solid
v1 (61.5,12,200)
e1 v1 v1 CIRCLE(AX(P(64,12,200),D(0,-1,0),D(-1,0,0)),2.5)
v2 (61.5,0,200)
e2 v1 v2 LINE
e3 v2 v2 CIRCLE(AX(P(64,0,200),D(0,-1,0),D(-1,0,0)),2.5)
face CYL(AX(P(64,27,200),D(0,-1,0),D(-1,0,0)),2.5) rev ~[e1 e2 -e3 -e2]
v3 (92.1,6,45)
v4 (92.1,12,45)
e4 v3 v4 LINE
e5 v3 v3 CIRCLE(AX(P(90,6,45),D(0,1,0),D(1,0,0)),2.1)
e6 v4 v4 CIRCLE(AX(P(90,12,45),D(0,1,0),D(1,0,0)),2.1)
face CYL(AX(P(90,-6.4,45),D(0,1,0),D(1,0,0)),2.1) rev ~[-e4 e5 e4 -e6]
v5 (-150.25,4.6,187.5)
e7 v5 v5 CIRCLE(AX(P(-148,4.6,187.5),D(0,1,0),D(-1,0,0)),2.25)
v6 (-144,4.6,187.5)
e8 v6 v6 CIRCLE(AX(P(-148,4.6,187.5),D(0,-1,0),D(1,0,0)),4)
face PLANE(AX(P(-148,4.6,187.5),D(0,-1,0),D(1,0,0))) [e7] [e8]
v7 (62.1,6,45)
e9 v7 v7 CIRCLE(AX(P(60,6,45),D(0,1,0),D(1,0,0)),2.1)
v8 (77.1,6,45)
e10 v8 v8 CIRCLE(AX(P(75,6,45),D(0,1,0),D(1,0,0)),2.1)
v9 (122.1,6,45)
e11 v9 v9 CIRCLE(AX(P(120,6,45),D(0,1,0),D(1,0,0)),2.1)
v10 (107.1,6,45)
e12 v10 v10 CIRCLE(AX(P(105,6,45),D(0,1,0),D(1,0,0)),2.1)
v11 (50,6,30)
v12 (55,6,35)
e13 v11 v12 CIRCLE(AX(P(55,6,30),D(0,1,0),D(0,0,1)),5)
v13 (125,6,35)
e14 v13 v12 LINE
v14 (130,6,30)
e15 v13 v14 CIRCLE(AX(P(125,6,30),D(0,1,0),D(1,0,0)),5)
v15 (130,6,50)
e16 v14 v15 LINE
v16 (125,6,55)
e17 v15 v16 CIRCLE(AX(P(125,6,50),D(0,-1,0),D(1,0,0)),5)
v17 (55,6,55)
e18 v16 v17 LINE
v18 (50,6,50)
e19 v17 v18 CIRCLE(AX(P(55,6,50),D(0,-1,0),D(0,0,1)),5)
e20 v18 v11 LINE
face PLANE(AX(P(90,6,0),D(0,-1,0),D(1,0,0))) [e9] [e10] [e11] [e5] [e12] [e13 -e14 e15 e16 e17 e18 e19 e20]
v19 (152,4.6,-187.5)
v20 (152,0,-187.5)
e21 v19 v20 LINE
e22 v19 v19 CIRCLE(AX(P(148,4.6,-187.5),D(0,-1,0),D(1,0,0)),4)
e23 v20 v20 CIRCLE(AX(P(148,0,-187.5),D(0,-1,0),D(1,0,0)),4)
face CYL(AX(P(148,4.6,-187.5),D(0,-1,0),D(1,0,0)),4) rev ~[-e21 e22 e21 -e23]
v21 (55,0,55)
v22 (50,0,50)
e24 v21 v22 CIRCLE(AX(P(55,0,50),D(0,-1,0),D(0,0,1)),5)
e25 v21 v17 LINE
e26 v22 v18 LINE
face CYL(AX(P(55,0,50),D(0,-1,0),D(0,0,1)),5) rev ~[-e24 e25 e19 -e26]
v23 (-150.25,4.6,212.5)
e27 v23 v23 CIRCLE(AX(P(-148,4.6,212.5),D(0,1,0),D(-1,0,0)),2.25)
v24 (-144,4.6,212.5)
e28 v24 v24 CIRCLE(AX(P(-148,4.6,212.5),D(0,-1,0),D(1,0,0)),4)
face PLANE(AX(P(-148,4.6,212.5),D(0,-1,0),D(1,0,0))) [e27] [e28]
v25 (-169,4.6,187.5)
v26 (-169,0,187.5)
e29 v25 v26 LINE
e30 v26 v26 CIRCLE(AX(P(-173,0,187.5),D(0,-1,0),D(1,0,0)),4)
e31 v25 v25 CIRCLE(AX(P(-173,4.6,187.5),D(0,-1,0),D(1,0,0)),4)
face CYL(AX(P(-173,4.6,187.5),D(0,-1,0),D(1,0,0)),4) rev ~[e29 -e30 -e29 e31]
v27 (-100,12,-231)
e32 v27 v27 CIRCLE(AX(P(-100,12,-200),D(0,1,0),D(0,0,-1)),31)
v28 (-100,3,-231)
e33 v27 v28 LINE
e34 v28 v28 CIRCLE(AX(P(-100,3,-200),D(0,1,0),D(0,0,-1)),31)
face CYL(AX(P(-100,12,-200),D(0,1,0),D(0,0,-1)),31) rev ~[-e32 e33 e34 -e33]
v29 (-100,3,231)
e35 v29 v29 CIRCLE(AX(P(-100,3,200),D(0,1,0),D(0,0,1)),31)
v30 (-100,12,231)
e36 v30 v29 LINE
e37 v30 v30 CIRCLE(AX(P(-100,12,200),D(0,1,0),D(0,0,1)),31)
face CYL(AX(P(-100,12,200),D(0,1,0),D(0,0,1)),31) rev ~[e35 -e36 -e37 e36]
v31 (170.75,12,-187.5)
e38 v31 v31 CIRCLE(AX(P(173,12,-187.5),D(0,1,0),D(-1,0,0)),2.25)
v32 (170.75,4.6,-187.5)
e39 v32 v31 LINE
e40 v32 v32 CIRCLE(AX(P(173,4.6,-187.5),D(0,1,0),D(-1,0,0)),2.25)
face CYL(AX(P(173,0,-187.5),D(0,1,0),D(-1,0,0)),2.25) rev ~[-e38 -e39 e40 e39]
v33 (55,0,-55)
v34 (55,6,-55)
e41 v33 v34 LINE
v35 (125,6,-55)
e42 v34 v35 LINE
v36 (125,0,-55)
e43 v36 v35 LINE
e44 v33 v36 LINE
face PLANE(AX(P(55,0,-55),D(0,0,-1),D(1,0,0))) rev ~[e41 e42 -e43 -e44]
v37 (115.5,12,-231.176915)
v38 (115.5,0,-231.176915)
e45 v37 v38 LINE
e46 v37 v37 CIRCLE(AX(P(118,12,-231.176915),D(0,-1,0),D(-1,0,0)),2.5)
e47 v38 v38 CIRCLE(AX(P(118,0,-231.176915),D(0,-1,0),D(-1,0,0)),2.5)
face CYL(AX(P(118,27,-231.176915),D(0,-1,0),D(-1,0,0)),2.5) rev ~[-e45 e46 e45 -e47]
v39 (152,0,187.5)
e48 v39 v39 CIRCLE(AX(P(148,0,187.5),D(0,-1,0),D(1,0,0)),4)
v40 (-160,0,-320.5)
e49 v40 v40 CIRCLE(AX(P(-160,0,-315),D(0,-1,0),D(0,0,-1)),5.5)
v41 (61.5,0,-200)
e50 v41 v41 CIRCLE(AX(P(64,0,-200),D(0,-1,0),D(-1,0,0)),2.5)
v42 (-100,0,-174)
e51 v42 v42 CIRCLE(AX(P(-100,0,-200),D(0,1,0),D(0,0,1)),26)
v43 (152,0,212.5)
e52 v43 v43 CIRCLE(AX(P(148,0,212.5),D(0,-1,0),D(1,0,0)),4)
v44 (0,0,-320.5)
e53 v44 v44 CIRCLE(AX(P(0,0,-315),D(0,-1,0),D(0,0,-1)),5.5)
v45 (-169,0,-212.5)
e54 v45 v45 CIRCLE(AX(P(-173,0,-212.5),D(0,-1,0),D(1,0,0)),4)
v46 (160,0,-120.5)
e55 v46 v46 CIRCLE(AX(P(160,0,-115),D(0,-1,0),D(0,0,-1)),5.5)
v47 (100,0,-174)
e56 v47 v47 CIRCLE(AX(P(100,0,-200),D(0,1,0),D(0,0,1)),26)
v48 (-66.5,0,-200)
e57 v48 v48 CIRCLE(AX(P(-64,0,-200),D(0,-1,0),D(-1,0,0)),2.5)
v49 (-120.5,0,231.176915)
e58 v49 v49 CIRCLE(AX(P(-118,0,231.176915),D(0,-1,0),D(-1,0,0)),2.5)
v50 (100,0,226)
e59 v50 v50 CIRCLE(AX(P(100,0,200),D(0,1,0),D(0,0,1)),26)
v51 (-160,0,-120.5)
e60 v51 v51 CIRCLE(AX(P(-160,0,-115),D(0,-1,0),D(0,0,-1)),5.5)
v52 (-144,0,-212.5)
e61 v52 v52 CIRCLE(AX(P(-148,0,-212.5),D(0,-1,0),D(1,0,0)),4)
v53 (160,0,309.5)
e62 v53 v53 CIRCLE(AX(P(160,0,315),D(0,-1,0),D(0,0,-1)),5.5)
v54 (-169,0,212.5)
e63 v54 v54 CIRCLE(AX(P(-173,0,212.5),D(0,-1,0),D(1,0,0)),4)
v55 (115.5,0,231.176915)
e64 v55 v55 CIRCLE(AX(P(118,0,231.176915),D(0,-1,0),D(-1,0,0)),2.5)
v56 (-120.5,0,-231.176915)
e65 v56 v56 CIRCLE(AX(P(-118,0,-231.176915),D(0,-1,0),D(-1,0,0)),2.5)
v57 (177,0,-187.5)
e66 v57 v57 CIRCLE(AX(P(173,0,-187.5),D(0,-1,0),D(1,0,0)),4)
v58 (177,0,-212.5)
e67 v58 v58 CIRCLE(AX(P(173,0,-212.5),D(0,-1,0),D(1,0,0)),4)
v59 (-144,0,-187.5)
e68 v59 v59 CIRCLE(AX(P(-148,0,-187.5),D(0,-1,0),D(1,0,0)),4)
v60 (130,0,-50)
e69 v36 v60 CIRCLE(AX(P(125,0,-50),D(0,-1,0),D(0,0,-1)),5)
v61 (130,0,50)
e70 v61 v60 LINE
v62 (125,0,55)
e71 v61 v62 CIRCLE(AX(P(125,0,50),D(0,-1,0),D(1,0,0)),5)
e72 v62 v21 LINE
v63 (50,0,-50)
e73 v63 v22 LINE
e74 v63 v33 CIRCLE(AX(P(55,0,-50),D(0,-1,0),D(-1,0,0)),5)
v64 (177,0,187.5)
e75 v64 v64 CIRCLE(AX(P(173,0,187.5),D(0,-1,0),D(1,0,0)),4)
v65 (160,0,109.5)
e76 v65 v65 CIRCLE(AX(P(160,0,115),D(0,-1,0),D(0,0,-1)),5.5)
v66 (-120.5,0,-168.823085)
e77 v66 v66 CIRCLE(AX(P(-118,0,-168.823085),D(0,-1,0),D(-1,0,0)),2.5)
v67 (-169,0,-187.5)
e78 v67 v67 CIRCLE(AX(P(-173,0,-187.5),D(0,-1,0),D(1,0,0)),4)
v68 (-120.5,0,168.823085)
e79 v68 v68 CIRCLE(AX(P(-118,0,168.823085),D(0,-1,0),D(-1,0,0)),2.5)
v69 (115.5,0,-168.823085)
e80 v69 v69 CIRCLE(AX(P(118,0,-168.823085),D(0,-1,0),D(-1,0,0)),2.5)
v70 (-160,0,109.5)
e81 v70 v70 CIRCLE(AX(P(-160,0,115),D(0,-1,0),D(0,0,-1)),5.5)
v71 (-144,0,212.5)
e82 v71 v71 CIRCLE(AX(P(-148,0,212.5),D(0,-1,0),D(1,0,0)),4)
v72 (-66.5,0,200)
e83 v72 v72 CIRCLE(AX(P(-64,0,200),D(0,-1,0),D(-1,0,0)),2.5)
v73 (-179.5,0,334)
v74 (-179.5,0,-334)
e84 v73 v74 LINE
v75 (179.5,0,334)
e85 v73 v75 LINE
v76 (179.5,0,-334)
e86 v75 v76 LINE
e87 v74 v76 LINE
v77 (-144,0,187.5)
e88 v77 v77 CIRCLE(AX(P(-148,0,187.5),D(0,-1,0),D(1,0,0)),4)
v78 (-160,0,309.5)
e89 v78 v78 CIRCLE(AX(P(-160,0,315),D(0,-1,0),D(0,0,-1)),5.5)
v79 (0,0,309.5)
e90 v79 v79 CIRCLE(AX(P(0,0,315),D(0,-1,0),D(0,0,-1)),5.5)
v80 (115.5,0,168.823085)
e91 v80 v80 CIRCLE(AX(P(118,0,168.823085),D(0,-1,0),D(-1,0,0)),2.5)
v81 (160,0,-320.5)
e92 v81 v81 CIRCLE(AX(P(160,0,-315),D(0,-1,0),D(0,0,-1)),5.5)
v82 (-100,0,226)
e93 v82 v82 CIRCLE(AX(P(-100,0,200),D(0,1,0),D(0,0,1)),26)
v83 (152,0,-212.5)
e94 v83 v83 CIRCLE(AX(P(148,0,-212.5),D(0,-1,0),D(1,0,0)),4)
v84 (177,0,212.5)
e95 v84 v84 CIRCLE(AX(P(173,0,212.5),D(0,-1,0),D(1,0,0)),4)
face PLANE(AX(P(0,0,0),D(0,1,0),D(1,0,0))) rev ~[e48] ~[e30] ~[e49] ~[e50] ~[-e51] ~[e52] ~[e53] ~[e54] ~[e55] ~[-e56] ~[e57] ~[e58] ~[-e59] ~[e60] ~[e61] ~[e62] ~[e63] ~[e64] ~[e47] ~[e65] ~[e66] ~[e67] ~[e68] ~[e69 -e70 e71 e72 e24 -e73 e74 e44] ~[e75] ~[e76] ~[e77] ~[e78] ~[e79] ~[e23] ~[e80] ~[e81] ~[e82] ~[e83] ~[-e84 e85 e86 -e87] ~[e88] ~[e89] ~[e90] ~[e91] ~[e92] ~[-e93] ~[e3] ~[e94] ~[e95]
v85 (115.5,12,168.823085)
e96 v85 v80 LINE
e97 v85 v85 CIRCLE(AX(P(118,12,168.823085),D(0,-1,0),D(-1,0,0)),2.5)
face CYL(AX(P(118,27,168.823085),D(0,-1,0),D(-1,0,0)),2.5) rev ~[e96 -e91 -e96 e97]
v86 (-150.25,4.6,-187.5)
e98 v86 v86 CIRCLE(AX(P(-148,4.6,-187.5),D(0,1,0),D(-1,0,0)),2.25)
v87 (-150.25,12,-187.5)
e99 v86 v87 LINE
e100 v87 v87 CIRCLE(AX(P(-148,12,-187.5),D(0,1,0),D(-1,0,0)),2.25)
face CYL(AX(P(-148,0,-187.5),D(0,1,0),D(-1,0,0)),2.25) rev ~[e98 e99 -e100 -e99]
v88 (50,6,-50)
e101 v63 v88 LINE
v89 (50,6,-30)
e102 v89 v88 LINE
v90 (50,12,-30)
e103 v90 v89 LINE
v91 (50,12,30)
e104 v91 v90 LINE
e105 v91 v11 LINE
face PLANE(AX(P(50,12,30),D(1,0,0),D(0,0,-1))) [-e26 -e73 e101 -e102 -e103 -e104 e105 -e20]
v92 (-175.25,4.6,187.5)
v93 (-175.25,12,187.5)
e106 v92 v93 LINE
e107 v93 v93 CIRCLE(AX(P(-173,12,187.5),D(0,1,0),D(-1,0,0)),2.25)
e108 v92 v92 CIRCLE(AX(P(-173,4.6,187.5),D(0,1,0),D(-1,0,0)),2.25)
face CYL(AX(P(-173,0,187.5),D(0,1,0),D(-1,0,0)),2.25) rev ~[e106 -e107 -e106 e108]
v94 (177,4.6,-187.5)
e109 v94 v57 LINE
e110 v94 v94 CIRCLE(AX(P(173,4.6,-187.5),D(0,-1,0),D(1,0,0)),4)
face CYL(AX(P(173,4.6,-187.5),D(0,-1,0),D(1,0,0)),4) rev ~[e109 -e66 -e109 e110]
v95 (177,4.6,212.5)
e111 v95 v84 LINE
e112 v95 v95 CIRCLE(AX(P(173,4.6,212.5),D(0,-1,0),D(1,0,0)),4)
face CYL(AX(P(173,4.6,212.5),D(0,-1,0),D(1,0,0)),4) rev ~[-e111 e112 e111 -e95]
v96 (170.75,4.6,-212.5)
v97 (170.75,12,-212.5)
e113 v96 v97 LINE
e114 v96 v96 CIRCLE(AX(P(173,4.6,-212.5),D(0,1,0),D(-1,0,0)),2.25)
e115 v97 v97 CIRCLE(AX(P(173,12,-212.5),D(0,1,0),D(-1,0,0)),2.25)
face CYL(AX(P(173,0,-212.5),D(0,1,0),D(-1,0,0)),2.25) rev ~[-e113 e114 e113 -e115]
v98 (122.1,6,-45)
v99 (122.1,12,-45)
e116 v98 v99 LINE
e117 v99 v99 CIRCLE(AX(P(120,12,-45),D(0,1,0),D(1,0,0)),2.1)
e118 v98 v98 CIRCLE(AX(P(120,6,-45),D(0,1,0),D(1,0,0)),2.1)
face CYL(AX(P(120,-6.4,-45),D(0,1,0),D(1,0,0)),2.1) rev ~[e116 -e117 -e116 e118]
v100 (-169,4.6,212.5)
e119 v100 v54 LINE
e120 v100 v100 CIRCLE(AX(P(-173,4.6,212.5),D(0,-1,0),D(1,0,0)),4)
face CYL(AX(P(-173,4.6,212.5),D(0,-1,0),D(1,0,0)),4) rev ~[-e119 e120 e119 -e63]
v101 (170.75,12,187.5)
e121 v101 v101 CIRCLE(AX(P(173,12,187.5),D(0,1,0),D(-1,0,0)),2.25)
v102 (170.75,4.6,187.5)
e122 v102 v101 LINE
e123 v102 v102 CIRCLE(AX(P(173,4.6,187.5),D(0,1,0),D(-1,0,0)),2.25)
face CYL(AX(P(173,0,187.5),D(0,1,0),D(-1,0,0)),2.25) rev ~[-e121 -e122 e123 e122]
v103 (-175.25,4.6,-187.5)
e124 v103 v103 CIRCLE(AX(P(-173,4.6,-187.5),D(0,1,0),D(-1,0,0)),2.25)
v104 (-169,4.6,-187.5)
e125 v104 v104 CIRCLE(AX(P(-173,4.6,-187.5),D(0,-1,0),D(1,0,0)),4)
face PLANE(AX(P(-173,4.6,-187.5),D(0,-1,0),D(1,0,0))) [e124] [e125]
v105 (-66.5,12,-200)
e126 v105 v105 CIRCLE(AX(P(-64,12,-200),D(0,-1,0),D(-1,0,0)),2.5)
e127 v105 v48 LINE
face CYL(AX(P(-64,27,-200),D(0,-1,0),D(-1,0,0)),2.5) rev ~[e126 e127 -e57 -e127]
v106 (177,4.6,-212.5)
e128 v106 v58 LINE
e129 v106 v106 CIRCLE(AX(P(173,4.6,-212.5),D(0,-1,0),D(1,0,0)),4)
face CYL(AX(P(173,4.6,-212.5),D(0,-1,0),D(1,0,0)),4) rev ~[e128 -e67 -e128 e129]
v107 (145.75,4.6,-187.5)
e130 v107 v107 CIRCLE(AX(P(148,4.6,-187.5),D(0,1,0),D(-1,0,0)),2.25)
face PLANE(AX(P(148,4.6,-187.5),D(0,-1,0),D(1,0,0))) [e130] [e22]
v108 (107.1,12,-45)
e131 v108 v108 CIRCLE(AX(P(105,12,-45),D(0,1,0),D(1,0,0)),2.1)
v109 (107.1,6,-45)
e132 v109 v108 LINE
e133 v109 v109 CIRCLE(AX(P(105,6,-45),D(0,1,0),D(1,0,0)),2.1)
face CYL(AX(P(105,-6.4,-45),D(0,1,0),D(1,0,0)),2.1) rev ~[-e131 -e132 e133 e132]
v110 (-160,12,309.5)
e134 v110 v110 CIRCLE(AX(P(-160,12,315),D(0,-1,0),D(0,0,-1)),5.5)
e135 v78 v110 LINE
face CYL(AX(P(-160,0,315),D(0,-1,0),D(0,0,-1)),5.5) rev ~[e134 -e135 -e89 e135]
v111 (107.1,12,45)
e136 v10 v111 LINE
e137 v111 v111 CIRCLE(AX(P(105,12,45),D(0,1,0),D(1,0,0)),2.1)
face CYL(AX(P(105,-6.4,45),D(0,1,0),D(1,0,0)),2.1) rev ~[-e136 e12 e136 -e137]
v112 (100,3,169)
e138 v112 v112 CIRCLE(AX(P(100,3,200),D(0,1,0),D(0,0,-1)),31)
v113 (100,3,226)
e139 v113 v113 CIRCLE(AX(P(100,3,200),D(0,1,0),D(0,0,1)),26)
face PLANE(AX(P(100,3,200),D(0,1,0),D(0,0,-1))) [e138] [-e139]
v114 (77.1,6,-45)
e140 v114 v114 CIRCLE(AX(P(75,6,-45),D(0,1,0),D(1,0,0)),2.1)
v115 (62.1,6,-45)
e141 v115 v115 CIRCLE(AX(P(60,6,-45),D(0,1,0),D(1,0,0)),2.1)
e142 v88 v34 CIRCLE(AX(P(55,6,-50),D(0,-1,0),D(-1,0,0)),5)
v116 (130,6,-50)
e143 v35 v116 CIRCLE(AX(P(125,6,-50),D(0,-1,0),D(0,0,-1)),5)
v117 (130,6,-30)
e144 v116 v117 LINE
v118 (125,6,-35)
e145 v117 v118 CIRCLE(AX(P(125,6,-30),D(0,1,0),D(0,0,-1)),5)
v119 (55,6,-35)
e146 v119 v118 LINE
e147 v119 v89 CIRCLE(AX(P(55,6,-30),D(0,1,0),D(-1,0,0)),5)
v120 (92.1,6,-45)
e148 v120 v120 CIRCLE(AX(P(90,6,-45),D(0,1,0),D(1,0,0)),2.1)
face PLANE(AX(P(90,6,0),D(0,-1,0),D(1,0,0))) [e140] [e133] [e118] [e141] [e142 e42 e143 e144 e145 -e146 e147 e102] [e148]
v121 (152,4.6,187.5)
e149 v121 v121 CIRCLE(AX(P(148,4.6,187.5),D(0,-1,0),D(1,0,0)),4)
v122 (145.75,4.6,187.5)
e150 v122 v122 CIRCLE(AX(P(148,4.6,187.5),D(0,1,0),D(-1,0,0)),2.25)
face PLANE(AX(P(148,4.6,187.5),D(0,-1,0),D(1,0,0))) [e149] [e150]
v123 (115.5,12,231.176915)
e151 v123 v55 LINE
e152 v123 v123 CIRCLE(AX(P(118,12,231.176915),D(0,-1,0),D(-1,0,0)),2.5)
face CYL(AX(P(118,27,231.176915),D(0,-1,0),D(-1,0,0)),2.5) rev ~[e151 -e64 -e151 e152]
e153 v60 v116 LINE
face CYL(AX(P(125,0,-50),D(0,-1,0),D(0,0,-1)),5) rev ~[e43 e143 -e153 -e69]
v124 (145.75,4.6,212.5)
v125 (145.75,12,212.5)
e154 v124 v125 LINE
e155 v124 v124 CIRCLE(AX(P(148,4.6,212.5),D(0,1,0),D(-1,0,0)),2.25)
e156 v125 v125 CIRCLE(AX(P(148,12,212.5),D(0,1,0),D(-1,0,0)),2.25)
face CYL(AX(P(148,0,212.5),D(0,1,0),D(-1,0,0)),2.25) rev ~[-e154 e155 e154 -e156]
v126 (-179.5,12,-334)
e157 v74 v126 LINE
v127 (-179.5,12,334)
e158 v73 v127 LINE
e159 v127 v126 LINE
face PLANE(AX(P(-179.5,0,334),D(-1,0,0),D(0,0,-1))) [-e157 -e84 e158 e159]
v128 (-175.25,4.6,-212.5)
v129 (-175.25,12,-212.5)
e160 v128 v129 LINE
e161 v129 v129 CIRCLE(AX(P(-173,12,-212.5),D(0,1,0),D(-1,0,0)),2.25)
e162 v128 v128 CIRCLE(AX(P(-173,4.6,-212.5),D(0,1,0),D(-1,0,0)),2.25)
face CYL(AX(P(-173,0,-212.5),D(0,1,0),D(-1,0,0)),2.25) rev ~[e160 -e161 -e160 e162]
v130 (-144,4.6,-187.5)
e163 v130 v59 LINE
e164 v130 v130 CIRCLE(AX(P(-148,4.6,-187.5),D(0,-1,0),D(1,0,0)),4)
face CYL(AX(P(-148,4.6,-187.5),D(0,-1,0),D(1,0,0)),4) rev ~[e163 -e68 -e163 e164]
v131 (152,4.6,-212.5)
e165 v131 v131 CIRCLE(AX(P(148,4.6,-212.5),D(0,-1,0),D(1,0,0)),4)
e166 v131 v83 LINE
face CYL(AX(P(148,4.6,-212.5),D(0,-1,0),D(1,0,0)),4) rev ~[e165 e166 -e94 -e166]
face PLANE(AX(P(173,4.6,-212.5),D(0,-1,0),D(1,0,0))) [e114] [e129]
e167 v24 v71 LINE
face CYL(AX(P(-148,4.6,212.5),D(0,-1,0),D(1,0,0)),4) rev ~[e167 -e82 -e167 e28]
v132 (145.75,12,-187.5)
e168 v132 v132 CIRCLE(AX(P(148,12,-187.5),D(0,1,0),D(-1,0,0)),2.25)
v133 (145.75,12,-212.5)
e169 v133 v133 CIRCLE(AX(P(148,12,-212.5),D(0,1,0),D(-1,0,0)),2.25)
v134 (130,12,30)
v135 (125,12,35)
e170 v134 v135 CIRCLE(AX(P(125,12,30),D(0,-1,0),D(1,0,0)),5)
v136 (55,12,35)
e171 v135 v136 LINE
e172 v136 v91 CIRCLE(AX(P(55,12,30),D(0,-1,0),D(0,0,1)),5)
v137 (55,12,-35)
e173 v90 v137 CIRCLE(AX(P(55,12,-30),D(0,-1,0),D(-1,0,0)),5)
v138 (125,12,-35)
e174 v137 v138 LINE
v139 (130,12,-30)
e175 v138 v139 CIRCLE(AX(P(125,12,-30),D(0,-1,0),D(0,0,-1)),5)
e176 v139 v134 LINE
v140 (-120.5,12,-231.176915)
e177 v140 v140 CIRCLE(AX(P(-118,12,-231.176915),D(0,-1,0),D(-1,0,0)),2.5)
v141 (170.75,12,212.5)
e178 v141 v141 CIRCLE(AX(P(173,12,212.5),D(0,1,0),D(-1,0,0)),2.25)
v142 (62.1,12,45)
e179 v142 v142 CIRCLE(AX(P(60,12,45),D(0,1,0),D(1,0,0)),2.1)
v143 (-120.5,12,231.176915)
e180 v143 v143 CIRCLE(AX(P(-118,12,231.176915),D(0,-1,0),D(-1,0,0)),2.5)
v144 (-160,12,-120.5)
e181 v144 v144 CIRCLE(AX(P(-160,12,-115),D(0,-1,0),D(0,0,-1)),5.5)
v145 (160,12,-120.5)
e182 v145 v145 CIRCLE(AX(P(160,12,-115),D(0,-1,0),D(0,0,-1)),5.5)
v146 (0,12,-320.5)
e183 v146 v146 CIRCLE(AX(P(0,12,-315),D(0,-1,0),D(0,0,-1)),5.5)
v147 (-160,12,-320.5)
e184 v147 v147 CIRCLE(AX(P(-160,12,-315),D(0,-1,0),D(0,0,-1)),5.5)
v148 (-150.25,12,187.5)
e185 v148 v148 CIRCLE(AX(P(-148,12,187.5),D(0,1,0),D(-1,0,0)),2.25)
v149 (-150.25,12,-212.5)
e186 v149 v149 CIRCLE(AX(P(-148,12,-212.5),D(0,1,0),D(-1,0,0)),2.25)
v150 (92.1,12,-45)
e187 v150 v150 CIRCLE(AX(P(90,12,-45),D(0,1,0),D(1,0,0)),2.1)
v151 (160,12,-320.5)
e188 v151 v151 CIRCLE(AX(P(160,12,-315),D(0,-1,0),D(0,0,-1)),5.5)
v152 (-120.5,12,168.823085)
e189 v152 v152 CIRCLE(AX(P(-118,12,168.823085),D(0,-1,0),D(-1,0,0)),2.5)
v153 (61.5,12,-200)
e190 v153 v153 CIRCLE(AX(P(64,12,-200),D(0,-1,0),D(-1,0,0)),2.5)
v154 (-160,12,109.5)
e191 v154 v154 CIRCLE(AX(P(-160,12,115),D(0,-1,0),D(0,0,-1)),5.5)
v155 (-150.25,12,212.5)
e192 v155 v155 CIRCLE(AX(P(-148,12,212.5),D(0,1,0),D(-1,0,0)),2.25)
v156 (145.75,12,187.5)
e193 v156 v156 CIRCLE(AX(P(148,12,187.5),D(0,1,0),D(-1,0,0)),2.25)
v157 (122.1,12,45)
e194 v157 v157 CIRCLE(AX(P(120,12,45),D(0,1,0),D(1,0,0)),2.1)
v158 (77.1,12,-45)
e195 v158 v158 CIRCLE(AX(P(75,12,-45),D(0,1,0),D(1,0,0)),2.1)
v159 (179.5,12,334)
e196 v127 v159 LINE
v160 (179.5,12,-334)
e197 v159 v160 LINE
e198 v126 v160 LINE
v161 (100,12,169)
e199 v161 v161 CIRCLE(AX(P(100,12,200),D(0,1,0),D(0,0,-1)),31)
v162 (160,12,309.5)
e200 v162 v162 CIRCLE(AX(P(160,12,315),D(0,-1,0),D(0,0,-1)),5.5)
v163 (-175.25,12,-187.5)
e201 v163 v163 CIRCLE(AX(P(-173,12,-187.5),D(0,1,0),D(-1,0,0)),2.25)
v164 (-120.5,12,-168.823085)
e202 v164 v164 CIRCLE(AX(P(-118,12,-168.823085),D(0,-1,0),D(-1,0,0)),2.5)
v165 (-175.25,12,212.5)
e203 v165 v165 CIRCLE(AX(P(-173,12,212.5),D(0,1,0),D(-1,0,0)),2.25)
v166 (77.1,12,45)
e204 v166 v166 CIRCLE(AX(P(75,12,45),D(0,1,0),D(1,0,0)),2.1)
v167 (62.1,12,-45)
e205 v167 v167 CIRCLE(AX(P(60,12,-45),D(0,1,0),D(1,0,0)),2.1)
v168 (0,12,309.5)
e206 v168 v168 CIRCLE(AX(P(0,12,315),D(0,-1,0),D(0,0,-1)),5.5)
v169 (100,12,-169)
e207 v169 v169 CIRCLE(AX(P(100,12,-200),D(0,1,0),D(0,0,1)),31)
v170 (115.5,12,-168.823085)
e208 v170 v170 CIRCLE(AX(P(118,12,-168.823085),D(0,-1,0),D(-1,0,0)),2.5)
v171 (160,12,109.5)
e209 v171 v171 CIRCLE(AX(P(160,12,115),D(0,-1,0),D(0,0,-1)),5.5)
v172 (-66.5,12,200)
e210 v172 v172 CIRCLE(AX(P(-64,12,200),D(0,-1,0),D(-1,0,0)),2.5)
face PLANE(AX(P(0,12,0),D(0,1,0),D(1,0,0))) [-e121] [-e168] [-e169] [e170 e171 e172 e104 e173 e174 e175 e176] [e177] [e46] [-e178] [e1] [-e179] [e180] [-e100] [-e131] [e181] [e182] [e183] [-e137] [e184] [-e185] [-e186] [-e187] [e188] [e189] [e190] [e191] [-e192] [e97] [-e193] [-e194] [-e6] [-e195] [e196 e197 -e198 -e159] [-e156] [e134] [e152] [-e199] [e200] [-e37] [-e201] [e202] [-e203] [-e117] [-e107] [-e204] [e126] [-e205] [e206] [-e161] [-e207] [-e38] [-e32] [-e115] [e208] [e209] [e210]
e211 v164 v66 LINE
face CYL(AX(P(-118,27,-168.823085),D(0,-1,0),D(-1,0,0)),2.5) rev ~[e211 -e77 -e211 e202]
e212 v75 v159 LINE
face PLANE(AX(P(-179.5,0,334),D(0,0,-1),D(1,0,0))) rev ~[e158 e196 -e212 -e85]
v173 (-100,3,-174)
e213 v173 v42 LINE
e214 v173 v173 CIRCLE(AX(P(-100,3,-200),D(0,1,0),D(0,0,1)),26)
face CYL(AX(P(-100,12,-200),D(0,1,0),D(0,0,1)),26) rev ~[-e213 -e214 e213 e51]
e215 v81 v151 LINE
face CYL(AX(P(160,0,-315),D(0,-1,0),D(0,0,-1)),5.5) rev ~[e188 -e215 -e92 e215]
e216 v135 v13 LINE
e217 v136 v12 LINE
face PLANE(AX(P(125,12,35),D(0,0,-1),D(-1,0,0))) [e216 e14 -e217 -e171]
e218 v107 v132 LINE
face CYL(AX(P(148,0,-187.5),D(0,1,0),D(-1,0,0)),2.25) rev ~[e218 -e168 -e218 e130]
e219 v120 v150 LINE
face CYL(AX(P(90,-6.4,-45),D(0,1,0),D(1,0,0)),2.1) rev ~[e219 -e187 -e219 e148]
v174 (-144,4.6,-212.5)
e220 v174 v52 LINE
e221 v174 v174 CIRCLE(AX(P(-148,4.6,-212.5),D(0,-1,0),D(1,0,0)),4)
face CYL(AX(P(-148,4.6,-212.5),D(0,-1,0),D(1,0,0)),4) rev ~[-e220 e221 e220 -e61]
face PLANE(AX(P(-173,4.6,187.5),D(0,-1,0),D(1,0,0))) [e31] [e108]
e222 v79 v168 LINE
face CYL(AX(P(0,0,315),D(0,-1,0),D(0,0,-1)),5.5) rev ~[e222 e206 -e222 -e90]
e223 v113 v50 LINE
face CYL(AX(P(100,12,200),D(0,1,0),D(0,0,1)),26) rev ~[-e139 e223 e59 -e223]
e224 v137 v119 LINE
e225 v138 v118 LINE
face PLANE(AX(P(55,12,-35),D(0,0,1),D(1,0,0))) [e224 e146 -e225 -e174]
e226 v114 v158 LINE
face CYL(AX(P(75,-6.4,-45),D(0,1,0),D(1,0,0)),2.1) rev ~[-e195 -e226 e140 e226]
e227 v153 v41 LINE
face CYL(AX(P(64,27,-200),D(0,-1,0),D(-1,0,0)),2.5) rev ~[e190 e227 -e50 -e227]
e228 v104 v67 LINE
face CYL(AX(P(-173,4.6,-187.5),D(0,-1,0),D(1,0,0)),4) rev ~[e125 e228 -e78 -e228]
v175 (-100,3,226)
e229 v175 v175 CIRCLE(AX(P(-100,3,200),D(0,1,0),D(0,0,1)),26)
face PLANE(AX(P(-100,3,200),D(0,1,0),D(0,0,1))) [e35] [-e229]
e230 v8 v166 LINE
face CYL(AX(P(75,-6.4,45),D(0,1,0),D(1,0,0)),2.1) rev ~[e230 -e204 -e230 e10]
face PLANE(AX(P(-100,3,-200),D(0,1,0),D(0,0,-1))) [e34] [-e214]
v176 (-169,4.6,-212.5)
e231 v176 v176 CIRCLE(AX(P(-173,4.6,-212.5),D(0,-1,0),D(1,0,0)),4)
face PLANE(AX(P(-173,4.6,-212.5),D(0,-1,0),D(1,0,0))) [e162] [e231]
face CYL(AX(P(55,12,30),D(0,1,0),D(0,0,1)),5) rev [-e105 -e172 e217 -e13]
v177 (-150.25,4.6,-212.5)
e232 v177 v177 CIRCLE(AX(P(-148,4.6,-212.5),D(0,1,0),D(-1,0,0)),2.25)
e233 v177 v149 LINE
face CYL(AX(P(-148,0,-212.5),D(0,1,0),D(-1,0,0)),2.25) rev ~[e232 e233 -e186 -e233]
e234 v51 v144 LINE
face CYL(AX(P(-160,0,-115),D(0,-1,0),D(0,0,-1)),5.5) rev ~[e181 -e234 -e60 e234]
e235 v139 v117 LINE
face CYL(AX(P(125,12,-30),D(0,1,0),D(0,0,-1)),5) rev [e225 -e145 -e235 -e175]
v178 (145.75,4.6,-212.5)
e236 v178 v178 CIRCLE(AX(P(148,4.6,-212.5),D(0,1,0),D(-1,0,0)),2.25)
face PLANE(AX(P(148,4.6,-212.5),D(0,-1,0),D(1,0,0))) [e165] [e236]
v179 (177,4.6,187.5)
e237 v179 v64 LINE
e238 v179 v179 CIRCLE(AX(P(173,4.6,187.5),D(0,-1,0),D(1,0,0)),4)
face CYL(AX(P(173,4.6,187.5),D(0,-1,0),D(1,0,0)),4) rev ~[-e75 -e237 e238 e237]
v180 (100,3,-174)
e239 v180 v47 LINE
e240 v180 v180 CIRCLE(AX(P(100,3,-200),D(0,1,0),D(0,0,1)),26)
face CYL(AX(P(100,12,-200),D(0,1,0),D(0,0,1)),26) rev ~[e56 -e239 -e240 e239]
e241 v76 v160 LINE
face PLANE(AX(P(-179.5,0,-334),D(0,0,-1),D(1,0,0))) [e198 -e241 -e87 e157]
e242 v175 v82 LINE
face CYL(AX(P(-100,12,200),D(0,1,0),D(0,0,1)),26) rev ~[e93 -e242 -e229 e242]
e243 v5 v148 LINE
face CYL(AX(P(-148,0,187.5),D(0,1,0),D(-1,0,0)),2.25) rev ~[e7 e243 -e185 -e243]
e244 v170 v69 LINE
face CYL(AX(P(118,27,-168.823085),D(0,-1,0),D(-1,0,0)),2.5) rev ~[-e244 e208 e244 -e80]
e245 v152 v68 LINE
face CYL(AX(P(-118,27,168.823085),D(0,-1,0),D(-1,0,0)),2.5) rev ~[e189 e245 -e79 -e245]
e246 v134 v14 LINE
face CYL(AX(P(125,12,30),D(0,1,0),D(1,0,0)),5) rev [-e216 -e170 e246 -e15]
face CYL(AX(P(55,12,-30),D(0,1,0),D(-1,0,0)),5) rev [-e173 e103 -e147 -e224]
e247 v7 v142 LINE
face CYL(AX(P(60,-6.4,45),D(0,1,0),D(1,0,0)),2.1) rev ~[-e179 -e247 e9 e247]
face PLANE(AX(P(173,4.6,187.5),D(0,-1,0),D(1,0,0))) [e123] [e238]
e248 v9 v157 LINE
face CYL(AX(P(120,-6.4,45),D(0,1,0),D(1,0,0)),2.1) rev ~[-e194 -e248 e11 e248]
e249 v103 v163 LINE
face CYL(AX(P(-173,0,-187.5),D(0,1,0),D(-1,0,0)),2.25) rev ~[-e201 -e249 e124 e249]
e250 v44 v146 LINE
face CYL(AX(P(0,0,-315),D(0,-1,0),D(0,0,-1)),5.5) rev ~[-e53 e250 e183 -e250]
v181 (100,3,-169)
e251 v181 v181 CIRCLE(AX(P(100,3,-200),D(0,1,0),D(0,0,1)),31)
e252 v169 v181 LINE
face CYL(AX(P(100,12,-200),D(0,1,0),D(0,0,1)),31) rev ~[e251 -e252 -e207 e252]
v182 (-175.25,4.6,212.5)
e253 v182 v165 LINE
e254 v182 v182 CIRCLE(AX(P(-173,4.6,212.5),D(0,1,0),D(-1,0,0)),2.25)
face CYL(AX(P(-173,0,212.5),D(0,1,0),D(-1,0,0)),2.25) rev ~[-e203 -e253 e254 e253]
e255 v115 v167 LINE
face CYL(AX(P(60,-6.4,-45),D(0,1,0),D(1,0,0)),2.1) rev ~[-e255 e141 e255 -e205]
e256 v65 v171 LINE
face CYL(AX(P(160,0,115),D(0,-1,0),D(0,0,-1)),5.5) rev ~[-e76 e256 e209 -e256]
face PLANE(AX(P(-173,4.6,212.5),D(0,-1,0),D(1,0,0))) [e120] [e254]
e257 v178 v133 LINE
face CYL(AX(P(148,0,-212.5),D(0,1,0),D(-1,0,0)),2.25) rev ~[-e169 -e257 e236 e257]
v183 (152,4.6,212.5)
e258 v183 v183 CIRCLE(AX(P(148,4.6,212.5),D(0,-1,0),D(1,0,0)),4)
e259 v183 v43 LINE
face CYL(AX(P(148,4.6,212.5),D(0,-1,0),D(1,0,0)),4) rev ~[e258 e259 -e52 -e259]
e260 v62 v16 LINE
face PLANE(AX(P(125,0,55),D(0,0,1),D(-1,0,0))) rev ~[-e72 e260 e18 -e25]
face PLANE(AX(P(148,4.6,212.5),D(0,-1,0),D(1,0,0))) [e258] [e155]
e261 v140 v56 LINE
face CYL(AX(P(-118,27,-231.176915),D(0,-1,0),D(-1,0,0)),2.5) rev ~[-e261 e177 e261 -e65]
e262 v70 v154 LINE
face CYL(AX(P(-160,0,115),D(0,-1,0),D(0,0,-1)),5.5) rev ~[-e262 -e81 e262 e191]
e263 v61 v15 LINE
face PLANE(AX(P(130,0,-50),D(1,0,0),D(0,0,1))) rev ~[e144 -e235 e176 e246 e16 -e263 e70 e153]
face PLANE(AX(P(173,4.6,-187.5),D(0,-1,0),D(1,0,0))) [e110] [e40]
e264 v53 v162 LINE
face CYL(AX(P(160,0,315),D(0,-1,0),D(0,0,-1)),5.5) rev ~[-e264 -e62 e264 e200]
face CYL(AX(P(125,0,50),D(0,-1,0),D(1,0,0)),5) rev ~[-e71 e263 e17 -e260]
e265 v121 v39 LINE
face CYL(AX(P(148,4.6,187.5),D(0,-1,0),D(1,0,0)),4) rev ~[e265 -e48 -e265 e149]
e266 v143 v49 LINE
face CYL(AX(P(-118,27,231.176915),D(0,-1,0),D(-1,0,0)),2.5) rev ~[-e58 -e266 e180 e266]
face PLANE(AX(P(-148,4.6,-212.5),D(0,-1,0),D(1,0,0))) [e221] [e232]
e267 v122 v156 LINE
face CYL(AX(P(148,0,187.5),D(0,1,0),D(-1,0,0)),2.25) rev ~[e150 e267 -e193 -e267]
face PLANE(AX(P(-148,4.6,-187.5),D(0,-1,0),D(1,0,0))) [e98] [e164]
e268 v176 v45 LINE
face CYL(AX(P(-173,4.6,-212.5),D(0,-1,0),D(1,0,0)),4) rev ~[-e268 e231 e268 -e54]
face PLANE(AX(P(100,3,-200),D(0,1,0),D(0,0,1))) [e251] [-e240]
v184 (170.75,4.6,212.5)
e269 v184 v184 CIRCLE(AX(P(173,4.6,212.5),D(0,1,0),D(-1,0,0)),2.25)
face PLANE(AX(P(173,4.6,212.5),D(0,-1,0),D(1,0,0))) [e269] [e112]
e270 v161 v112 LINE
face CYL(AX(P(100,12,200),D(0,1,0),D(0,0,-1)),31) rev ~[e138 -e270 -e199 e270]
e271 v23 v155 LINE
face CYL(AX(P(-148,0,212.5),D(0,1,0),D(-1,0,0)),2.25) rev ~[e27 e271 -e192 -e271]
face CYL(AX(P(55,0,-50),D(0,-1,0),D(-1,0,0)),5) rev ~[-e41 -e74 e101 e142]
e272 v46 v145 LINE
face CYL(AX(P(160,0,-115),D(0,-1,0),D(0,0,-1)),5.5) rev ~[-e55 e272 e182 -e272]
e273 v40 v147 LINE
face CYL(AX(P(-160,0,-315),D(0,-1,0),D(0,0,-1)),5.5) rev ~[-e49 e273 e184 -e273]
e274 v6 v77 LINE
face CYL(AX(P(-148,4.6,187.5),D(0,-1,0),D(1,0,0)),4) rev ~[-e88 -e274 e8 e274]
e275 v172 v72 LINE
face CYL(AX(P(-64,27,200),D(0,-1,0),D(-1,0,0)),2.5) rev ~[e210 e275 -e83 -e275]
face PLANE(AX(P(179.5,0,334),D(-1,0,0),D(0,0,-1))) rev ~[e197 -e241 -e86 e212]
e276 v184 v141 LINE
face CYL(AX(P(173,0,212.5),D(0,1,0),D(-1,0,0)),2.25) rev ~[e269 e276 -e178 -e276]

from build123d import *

# Parameters (mm, degrees)
SKETCH1_W                                          = 359
SKETCH1_H                                          = 668
BOSS_EXTRUDE1_DEPTH                                = 12
HOLE_SIZE_BASED_ON_SOCKET_HEAD_CAP_SCR_D           = 4.5
HOLE_SIZE_BASED_ON_SOCKET_HEAD_CAP_SCR_CBORE_D     = 8
HOLE_SIZE_BASED_ON_SOCKET_HEAD_CAP_SCR_CBORE_DEPTH = 4.6
SKETCH5_R                                          = 31
CUT_EXTRUDE2_DEPTH                                 = 9
SKETCH7_R                                          = 26
CUT_EXTRUDE4_DEPTH                                 = 380.368224816
M6_TAPPED_HOLE1_D                                  = 5
M6_TAPPED_HOLE1_DEPTH                              = 15
M6_TAPPED_HOLE1_TIP                                = 1.502151548
SKETCH12_R                                         = 5.5
CUT_EXTRUDE5_DEPTH                                 = 380.368224816
CUT_EXTRUDE6_DEPTH                                 = 380.368224816
CUT_EXTRUDE8_DEPTH                                 = 6
M5_TAPPED_HOLE1_D                                  = 4.2
M5_TAPPED_HOLE1_DEPTH                              = 12.4
M5_TAPPED_HOLE1_TIP                                = 1.2618073


with BuildPart() as part:
    # Sketch1 → Boss-Extrude1 (new body)
    with BuildSketch(Plane(origin=(0, 0, 0), x_dir=(1, 0, 0), z_dir=(0, 1, 0))):
        Rectangle(SKETCH1_W, SKETCH1_H)
    extrude(amount=BOSS_EXTRUDE1_DEPTH)

    # Hole size (%based on) socket head cap screw type 1 (through all)
    with Locations(Plane.XZ):
        with Locations((-173, 212.5), (-148, 212.5), (-148, 187.5), (-173, 187.5), (-173, -187.5), (-148, -187.5), (-148, -212.5), (-173, -212.5), (173, -212.5), (148, -212.5), (148, -187.5), (173, -187.5), (173, 187.5), (148, 187.5), (148, 212.5), (173, 212.5)):
            CounterBoreHole(HOLE_SIZE_BASED_ON_SOCKET_HEAD_CAP_SCR_D / 2, HOLE_SIZE_BASED_ON_SOCKET_HEAD_CAP_SCR_CBORE_D / 2, HOLE_SIZE_BASED_ON_SOCKET_HEAD_CAP_SCR_CBORE_DEPTH)

    # Sketch5 → Cut-Extrude2 (cut)
    with BuildSketch(Plane(origin=(0, 12, 0), x_dir=(1, 0, 0), z_dir=(0, 1, 0))):
        with Locations(Location((-100, -200, 0), (0, 0, 270))):
            Circle(SKETCH5_R)
        with Locations(Location((100, -200, 0), (0, 0, 90))):
            Circle(SKETCH5_R)
        with Locations(Location((100, 200, 0), (0, 0, 270))):
            Circle(SKETCH5_R)
        with Locations(Location((-100, 200, 0), (0, 0, 90))):
            Circle(SKETCH5_R)
    extrude(amount=-CUT_EXTRUDE2_DEPTH, mode=Mode.SUBTRACT)

    # Sketch7 → Cut-Extrude4 (cut, through all)
    with BuildSketch(Plane(origin=(0, 12, 0), x_dir=(1, 0, 0), z_dir=(0, 1, 0))):
        with Locations(Location((-100, 200, 0), (0, 0, 270))):
            Circle(SKETCH7_R)
        with Locations(Location((100, 200, 0), (0, 0, 270))):
            Circle(SKETCH7_R)
        with Locations(Location((100, -200, 0), (0, 0, 270))):
            Circle(SKETCH7_R)
        with Locations(Location((-100, -200, 0), (0, 0, 270))):
            Circle(SKETCH7_R)
    extrude(amount=-CUT_EXTRUDE4_DEPTH, mode=Mode.SUBTRACT)

    # M6 Tapped Hole1
    with Locations(Plane(origin=(0, 12, 0), x_dir=(1, 0, 0), z_dir=(0, 1, 0))):
        with Locations((-118, 231.176914536), (-64, 200), (-118, 168.823085464), (118, 168.823085464), (64, 200), (118, 231.176914536), (118, -231.176914536), (64, -200), (118, -168.823085464), (-118, -168.823085464), (-64, -200), (-118, -231.176914536)):
            Hole(M6_TAPPED_HOLE1_D / 2, depth=M6_TAPPED_HOLE1_DEPTH)
            with Locations((0, 0, -(M6_TAPPED_HOLE1_DEPTH + M6_TAPPED_HOLE1_TIP / 2))):  # 118° drill point
                Cone(0, M6_TAPPED_HOLE1_D / 2, M6_TAPPED_HOLE1_TIP, mode=Mode.SUBTRACT)

    # Sketch12 → Cut-Extrude5 (cut, through all)
    with BuildSketch(Plane.XZ):
        with Locations(Location((-160, 315, 0), (0, 0, 270))):
            Circle(SKETCH12_R)
        with Locations(Location((0, 315, 0), (0, 0, 270))):
            Circle(SKETCH12_R)
        with Locations(Location((-160, 115, 0), (0, 0, 270))):
            Circle(SKETCH12_R)
        with Locations(Location((-160, -115, 0), (0, 0, 270))):
            Circle(SKETCH12_R)
        with Locations(Location((-160, -315, 0), (0, 0, 270))):
            Circle(SKETCH12_R)
        with Locations(Location((0, -315, 0), (0, 0, 270))):
            Circle(SKETCH12_R)
        with Locations(Location((160, -315, 0), (0, 0, 270))):
            Circle(SKETCH12_R)
        with Locations(Location((160, -115, 0), (0, 0, 270))):
            Circle(SKETCH12_R)
        with Locations(Location((160, 115, 0), (0, 0, 270))):
            Circle(SKETCH12_R)
        with Locations(Location((160, 315, 0), (0, 0, 270))):
            Circle(SKETCH12_R)
    extrude(amount=-CUT_EXTRUDE5_DEPTH, mode=Mode.SUBTRACT)

    # Sketch13 → Cut-Extrude6 (cut, through all)
    with BuildSketch(Plane(origin=(0, 12, 0), x_dir=(1, 0, 0), z_dir=(0, 1, 0))):
        with BuildLine():
            Line((55, 35), (125, 35))
            ThreePointArc((125, 35), (128.535533906, 33.535533906), (130, 30))
            Line((130, 30), (130, -30))
            ThreePointArc((130, -30), (128.535533906, -33.535533906), (125, -35))
            Line((125, -35), (55, -35))
            ThreePointArc((55, -35), (51.464466094, -33.535533906), (50, -30))
            Line((50, -30), (50, 30))
            ThreePointArc((50, 30), (51.464466094, 33.535533906), (55, 35))
        make_face()
    extrude(amount=-CUT_EXTRUDE6_DEPTH, mode=Mode.SUBTRACT)

    # Sketch17 → Cut-Extrude8 (cut)
    with BuildSketch(Plane.XZ):
        with BuildLine():
            Line((55, -55), (125, -55))
            ThreePointArc((125, -55), (128.535533906, -53.535533906), (130, -50))
            Line((130, -50), (130, 50))
            ThreePointArc((130, 50), (128.535533906, 53.535533906), (125, 55))
            Line((125, 55), (55, 55))
            ThreePointArc((55, 55), (51.464466094, 53.535533906), (50, 50))
            Line((50, 50), (50, -50))
            ThreePointArc((50, -50), (51.464466094, -53.535533906), (55, -55))
        make_face()
    extrude(amount=-CUT_EXTRUDE8_DEPTH, mode=Mode.SUBTRACT)

    # M5 Tapped Hole1
    with Locations(Plane(origin=(0, 6, 0), x_dir=(-1, 0, 0), z_dir=(0, -1, 0))):
        with Locations((-120, 45), (-105, 45), (-90, 45), (-75, 45), (-60, 45), (-60, -45), (-75, -45), (-90, -45), (-105, -45), (-120, -45)):
            Hole(M5_TAPPED_HOLE1_D / 2, depth=M5_TAPPED_HOLE1_DEPTH)
            with Locations((0, 0, -(M5_TAPPED_HOLE1_DEPTH + M5_TAPPED_HOLE1_TIP / 2))):  # 118° drill point
                Cone(0, M5_TAPPED_HOLE1_D / 2, M5_TAPPED_HOLE1_TIP, mode=Mode.SUBTRACT)


solid = part.part
